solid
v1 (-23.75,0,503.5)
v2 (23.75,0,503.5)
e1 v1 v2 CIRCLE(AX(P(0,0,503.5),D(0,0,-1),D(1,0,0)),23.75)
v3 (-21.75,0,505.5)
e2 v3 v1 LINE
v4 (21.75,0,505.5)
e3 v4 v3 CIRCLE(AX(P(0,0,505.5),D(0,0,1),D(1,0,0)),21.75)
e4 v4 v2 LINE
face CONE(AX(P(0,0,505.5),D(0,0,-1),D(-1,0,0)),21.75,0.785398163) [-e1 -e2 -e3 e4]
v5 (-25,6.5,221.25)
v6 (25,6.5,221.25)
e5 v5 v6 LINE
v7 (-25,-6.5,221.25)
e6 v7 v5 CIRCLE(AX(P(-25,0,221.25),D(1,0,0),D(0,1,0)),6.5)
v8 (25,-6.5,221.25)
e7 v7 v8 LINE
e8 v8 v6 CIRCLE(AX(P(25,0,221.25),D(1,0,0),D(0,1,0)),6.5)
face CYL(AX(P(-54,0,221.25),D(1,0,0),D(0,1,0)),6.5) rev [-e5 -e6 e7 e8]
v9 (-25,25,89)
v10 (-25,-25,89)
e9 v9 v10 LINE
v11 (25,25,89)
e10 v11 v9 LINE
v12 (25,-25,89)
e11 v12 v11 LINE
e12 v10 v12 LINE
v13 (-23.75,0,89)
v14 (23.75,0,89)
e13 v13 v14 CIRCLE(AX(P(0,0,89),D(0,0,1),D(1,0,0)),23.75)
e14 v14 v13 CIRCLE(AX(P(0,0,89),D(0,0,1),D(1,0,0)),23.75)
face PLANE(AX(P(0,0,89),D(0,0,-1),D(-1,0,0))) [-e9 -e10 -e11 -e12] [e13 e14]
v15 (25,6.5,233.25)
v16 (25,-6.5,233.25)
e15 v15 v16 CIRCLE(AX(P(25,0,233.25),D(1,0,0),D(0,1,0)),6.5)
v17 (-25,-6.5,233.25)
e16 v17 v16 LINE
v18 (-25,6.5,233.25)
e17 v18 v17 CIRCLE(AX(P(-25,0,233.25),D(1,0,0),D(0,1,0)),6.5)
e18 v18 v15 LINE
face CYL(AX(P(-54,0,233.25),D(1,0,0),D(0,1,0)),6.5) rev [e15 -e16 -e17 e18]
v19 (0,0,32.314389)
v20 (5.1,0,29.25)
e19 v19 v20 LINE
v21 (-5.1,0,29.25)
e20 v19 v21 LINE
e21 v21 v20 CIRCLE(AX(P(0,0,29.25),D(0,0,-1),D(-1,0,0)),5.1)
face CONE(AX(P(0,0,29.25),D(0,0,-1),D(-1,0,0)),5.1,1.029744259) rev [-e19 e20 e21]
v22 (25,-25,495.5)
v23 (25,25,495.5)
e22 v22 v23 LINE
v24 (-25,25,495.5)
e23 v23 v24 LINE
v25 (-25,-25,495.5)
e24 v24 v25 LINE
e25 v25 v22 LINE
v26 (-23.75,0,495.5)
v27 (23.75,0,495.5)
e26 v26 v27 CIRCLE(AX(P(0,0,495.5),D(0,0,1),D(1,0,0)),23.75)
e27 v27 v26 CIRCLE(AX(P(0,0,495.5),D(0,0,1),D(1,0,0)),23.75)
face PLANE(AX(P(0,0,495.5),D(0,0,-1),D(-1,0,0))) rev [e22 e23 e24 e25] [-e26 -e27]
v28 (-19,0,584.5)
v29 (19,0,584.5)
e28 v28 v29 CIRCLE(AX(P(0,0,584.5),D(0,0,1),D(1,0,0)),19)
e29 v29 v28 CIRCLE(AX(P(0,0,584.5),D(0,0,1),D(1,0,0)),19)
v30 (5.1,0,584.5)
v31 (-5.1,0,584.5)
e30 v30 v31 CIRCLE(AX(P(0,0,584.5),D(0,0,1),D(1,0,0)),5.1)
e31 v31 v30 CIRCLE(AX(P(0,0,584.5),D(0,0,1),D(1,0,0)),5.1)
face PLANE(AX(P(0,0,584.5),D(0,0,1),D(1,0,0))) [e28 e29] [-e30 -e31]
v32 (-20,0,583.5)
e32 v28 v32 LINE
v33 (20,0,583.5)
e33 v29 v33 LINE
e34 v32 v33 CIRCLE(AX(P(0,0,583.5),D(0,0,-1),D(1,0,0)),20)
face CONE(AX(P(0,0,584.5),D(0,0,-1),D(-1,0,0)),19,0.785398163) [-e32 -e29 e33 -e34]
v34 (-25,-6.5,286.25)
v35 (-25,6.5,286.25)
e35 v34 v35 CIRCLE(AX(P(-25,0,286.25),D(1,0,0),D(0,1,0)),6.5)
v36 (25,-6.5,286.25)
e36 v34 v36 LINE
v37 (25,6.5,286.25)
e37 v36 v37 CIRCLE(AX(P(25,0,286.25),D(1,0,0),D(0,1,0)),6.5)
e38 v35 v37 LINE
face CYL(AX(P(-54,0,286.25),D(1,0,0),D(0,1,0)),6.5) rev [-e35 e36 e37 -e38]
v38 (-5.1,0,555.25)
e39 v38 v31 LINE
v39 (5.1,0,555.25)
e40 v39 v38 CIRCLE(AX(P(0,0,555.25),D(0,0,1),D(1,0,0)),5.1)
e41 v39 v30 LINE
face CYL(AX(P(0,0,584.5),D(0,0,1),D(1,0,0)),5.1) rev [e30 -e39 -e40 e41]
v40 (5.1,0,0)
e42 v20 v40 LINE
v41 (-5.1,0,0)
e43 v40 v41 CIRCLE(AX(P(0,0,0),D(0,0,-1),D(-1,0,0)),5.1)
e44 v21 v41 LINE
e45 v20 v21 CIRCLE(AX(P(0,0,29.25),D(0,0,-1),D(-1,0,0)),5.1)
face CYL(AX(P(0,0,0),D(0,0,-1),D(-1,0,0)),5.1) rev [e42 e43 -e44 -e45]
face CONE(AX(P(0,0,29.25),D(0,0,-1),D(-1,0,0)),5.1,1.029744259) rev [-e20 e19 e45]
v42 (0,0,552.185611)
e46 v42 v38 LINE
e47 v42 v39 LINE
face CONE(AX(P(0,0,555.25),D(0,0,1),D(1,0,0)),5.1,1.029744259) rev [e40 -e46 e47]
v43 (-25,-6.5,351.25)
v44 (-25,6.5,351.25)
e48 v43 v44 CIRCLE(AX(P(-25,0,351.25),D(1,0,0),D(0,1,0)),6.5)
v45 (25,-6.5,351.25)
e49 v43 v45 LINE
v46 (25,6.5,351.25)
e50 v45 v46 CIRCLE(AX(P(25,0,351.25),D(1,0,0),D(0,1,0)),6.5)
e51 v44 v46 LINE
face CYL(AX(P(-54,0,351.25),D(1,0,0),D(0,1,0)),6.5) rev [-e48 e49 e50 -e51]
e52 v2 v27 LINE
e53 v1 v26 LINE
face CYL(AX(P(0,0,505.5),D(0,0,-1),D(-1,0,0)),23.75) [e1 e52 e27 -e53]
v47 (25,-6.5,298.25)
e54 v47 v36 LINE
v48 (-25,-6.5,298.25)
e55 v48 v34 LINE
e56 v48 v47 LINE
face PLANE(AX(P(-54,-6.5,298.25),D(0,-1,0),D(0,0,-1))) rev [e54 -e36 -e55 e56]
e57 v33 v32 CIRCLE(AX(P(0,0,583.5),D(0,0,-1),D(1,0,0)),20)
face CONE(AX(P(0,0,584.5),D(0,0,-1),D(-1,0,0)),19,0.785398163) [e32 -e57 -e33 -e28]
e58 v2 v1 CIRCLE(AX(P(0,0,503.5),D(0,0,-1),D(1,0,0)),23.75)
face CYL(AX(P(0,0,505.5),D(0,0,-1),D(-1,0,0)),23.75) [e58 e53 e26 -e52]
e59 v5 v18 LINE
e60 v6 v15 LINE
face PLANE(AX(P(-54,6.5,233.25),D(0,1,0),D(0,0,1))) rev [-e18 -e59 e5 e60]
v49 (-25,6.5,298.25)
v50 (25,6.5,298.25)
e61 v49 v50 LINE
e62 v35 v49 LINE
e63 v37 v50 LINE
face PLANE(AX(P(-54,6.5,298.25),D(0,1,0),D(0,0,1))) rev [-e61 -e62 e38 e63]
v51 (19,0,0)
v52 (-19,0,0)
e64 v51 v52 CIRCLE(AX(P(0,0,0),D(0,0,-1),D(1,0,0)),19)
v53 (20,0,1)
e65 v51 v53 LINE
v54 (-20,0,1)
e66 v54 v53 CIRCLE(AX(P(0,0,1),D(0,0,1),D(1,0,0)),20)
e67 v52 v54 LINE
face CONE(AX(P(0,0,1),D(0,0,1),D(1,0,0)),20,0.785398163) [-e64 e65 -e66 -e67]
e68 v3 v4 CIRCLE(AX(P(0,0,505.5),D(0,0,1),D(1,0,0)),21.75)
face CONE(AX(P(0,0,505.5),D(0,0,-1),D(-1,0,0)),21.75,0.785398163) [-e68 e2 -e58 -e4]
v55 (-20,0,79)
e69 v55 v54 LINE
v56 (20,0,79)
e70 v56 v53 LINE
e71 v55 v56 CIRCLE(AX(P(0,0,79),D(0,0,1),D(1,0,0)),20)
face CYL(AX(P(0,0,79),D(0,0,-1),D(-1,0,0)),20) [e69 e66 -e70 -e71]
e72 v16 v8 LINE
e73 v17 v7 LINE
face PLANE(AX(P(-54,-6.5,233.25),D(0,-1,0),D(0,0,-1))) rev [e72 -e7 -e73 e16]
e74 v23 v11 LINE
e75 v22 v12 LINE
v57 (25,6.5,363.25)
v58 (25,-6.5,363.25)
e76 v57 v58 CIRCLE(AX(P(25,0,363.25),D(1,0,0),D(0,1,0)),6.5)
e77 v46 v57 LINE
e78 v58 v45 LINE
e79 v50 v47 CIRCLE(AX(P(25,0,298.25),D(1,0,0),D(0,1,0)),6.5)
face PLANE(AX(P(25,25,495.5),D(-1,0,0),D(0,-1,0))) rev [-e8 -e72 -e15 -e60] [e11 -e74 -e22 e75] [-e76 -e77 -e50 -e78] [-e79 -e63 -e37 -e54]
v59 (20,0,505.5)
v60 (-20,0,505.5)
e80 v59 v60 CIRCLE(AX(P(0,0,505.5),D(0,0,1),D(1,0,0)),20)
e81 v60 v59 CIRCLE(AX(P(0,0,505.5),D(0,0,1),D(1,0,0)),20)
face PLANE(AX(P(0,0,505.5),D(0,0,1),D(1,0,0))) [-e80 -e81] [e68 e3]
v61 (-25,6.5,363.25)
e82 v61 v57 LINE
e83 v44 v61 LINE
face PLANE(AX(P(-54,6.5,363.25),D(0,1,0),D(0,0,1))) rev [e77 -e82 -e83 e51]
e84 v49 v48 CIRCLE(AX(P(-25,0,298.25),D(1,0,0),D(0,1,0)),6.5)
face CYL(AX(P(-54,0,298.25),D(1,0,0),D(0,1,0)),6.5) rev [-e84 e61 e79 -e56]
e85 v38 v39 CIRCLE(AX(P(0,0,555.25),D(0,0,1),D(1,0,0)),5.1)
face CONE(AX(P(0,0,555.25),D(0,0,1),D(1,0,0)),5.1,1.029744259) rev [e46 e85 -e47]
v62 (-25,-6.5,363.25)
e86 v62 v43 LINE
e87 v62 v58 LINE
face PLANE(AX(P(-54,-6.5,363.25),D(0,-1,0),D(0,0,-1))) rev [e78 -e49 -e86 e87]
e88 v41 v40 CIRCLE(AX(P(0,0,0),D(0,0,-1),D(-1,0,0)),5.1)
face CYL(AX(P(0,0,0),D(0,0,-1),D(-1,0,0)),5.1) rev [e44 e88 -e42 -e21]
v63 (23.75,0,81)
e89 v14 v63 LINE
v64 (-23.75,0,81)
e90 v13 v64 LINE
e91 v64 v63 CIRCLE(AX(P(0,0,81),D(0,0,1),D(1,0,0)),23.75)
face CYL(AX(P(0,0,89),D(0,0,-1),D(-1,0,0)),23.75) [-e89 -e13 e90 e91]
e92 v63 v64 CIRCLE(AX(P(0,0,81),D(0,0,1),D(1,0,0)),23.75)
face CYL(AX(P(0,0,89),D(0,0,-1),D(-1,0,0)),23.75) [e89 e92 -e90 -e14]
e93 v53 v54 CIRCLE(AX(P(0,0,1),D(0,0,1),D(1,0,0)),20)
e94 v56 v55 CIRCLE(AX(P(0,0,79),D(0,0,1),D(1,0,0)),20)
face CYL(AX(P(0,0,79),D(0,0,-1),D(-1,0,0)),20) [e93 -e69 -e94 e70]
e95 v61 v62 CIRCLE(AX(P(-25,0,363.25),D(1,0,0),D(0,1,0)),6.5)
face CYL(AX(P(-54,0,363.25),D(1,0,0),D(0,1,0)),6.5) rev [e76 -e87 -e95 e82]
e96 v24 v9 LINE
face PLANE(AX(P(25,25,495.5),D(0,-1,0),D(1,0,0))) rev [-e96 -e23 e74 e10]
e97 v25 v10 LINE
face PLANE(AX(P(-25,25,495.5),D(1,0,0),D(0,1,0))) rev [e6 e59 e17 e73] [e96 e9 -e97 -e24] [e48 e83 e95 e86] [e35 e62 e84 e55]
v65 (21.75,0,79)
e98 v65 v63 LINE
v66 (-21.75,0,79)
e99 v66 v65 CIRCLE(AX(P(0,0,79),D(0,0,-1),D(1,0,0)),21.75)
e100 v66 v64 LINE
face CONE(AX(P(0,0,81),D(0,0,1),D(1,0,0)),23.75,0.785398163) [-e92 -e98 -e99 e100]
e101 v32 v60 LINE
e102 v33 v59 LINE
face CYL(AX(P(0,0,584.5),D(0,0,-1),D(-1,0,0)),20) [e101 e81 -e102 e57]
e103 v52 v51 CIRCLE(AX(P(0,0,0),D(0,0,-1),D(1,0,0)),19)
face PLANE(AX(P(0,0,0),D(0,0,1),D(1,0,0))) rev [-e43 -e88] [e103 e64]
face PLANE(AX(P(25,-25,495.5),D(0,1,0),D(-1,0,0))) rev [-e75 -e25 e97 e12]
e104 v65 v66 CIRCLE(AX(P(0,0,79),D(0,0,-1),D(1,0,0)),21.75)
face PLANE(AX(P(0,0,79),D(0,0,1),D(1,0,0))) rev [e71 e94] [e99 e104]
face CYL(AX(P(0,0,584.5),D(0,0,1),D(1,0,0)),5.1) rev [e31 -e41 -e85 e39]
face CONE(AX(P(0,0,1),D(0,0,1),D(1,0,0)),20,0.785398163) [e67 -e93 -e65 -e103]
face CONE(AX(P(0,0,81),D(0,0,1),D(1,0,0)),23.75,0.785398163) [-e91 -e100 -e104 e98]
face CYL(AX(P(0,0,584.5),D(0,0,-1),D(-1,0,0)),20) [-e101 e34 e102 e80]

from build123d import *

# Parameters (mm, degrees)
SKETCH_1_R              = 20
EXTRUDE_1_DEPTH         = 79
SKETCH_2_R              = 23.75
EXTRUDE_2_DEPTH         = 10
CHAMFER_1_SIZE          = 2
SKETCH_3_W              = 50
SKETCH_3_H              = 50
EXTRUDE_3_DEPTH         = 406.5
SKETCH_4_R              = 23.75
EXTRUDE_4_DEPTH         = 10
CHAMFER_2_SIZE          = 2
SKETCH_5_R              = 20
EXTRUDE_5_DEPTH         = 79
CHAMFER_3_SIZE          = 1
HOLE_WIZARD_M12_1_D     = 10.2
HOLE_WIZARD_M12_1_DEPTH = 29.25
HOLE_WIZARD_M12_1_TIP   = 3.064389157
HOLE_WIZARD_M12_2_D     = 10.2
HOLE_WIZARD_M12_2_DEPTH = 29.25
HOLE_WIZARD_M12_2_TIP   = 3.064389157
CUT_EXTRUDE_1_DEPTH     = 79


with BuildPart() as part:
    # 草图1 → 凸台-拉伸1 (new body)
    with BuildSketch(Plane.XY):
        Circle(SKETCH_1_R)
    extrude(amount=EXTRUDE_1_DEPTH)

    # 草图2 → 凸台-拉伸2 (add)
    with BuildSketch(Plane.XY.offset(79)):
        Circle(SKETCH_2_R)
    extrude(amount=EXTRUDE_2_DEPTH)

    # 倒角1
    chamfer_1_edges = [part.edges().sort_by_distance(p)[0] for p in [
        (-23.75, 0, 79),
    ]]
    chamfer(chamfer_1_edges, length=CHAMFER_1_SIZE)

    # 草图3 → 凸台-拉伸3 (add)
    with BuildSketch(Plane.XY.offset(89)):
        Rectangle(SKETCH_3_W, SKETCH_3_H)
    extrude(amount=EXTRUDE_3_DEPTH)

    # 草图4 → 凸台-拉伸4 (add)
    with BuildSketch(Plane.XY.offset(495.5)):
        Circle(SKETCH_4_R)
    extrude(amount=EXTRUDE_4_DEPTH)

    # 倒角2
    chamfer_2_edges = [part.edges().sort_by_distance(p)[0] for p in [
        (-23.75, 0, 505.5),
    ]]
    chamfer(chamfer_2_edges, length=CHAMFER_2_SIZE)

    # 草图5 → 凸台-拉伸5 (add)
    with BuildSketch(Plane.XY.offset(505.5)):
        Circle(SKETCH_5_R)
    extrude(amount=EXTRUDE_5_DEPTH)

    # 倒角3
    chamfer_3_edges = [part.edges().sort_by_distance(p)[0] for p in [
        (-20, 0, 0),
        (-20, 0, 584.5),
    ]]
    chamfer(chamfer_3_edges, length=CHAMFER_3_SIZE)

    # M12 螺纹孔1
    with Locations(Plane(origin=(0, 0, 0), x_dir=(-1, 0, 0), z_dir=(0, 0, -1))):
        with Locations((0, 0)):
            Hole(HOLE_WIZARD_M12_1_D / 2, depth=HOLE_WIZARD_M12_1_DEPTH)
            with Locations((0, 0, -(HOLE_WIZARD_M12_1_DEPTH + HOLE_WIZARD_M12_1_TIP / 2))):  # 118° drill point
                Cone(0, HOLE_WIZARD_M12_1_D / 2, HOLE_WIZARD_M12_1_TIP, mode=Mode.SUBTRACT)

    # M12 螺纹孔2
    with Locations(Plane.XY.offset(584.5)):
        with Locations((0, 0)):
            Hole(HOLE_WIZARD_M12_2_D / 2, depth=HOLE_WIZARD_M12_2_DEPTH)
            with Locations((0, 0, -(HOLE_WIZARD_M12_2_DEPTH + HOLE_WIZARD_M12_2_TIP / 2))):  # 118° drill point
                Cone(0, HOLE_WIZARD_M12_2_D / 2, HOLE_WIZARD_M12_2_TIP, mode=Mode.SUBTRACT)

    # 草图10 → 切除-拉伸1 (cut)
    with BuildSketch(Plane(origin=(25, 0, 0), x_dir=(0, 0, -1), z_dir=(1, 0, 0))):
        with BuildLine():
            Line((-363.25, 6.5), (-351.25, 6.5))
            ThreePointArc((-351.25, 6.5), (-344.75, 0), (-351.25, -6.5))
            Line((-351.25, -6.5), (-363.25, -6.5))
            ThreePointArc((-363.25, -6.5), (-369.75, 0), (-363.25, 6.5))
        make_face()
        with BuildLine():
            Line((-298.25, 6.5), (-286.25, 6.5))
            ThreePointArc((-286.25, 6.5), (-279.75, 0), (-286.25, -6.5))
            Line((-286.25, -6.5), (-298.25, -6.5))
            ThreePointArc((-298.25, -6.5), (-304.75, 0), (-298.25, 6.5))
        make_face()
        with BuildLine():
            Line((-233.25, 6.5), (-221.25, 6.5))
            ThreePointArc((-221.25, 6.5), (-214.75, 0), (-221.25, -6.5))
            Line((-221.25, -6.5), (-233.25, -6.5))
            ThreePointArc((-233.25, -6.5), (-239.75, 0), (-233.25, 6.5))
        make_face()
    extrude(amount=-CUT_EXTRUDE_1_DEPTH, mode=Mode.SUBTRACT)


solid = part.part
